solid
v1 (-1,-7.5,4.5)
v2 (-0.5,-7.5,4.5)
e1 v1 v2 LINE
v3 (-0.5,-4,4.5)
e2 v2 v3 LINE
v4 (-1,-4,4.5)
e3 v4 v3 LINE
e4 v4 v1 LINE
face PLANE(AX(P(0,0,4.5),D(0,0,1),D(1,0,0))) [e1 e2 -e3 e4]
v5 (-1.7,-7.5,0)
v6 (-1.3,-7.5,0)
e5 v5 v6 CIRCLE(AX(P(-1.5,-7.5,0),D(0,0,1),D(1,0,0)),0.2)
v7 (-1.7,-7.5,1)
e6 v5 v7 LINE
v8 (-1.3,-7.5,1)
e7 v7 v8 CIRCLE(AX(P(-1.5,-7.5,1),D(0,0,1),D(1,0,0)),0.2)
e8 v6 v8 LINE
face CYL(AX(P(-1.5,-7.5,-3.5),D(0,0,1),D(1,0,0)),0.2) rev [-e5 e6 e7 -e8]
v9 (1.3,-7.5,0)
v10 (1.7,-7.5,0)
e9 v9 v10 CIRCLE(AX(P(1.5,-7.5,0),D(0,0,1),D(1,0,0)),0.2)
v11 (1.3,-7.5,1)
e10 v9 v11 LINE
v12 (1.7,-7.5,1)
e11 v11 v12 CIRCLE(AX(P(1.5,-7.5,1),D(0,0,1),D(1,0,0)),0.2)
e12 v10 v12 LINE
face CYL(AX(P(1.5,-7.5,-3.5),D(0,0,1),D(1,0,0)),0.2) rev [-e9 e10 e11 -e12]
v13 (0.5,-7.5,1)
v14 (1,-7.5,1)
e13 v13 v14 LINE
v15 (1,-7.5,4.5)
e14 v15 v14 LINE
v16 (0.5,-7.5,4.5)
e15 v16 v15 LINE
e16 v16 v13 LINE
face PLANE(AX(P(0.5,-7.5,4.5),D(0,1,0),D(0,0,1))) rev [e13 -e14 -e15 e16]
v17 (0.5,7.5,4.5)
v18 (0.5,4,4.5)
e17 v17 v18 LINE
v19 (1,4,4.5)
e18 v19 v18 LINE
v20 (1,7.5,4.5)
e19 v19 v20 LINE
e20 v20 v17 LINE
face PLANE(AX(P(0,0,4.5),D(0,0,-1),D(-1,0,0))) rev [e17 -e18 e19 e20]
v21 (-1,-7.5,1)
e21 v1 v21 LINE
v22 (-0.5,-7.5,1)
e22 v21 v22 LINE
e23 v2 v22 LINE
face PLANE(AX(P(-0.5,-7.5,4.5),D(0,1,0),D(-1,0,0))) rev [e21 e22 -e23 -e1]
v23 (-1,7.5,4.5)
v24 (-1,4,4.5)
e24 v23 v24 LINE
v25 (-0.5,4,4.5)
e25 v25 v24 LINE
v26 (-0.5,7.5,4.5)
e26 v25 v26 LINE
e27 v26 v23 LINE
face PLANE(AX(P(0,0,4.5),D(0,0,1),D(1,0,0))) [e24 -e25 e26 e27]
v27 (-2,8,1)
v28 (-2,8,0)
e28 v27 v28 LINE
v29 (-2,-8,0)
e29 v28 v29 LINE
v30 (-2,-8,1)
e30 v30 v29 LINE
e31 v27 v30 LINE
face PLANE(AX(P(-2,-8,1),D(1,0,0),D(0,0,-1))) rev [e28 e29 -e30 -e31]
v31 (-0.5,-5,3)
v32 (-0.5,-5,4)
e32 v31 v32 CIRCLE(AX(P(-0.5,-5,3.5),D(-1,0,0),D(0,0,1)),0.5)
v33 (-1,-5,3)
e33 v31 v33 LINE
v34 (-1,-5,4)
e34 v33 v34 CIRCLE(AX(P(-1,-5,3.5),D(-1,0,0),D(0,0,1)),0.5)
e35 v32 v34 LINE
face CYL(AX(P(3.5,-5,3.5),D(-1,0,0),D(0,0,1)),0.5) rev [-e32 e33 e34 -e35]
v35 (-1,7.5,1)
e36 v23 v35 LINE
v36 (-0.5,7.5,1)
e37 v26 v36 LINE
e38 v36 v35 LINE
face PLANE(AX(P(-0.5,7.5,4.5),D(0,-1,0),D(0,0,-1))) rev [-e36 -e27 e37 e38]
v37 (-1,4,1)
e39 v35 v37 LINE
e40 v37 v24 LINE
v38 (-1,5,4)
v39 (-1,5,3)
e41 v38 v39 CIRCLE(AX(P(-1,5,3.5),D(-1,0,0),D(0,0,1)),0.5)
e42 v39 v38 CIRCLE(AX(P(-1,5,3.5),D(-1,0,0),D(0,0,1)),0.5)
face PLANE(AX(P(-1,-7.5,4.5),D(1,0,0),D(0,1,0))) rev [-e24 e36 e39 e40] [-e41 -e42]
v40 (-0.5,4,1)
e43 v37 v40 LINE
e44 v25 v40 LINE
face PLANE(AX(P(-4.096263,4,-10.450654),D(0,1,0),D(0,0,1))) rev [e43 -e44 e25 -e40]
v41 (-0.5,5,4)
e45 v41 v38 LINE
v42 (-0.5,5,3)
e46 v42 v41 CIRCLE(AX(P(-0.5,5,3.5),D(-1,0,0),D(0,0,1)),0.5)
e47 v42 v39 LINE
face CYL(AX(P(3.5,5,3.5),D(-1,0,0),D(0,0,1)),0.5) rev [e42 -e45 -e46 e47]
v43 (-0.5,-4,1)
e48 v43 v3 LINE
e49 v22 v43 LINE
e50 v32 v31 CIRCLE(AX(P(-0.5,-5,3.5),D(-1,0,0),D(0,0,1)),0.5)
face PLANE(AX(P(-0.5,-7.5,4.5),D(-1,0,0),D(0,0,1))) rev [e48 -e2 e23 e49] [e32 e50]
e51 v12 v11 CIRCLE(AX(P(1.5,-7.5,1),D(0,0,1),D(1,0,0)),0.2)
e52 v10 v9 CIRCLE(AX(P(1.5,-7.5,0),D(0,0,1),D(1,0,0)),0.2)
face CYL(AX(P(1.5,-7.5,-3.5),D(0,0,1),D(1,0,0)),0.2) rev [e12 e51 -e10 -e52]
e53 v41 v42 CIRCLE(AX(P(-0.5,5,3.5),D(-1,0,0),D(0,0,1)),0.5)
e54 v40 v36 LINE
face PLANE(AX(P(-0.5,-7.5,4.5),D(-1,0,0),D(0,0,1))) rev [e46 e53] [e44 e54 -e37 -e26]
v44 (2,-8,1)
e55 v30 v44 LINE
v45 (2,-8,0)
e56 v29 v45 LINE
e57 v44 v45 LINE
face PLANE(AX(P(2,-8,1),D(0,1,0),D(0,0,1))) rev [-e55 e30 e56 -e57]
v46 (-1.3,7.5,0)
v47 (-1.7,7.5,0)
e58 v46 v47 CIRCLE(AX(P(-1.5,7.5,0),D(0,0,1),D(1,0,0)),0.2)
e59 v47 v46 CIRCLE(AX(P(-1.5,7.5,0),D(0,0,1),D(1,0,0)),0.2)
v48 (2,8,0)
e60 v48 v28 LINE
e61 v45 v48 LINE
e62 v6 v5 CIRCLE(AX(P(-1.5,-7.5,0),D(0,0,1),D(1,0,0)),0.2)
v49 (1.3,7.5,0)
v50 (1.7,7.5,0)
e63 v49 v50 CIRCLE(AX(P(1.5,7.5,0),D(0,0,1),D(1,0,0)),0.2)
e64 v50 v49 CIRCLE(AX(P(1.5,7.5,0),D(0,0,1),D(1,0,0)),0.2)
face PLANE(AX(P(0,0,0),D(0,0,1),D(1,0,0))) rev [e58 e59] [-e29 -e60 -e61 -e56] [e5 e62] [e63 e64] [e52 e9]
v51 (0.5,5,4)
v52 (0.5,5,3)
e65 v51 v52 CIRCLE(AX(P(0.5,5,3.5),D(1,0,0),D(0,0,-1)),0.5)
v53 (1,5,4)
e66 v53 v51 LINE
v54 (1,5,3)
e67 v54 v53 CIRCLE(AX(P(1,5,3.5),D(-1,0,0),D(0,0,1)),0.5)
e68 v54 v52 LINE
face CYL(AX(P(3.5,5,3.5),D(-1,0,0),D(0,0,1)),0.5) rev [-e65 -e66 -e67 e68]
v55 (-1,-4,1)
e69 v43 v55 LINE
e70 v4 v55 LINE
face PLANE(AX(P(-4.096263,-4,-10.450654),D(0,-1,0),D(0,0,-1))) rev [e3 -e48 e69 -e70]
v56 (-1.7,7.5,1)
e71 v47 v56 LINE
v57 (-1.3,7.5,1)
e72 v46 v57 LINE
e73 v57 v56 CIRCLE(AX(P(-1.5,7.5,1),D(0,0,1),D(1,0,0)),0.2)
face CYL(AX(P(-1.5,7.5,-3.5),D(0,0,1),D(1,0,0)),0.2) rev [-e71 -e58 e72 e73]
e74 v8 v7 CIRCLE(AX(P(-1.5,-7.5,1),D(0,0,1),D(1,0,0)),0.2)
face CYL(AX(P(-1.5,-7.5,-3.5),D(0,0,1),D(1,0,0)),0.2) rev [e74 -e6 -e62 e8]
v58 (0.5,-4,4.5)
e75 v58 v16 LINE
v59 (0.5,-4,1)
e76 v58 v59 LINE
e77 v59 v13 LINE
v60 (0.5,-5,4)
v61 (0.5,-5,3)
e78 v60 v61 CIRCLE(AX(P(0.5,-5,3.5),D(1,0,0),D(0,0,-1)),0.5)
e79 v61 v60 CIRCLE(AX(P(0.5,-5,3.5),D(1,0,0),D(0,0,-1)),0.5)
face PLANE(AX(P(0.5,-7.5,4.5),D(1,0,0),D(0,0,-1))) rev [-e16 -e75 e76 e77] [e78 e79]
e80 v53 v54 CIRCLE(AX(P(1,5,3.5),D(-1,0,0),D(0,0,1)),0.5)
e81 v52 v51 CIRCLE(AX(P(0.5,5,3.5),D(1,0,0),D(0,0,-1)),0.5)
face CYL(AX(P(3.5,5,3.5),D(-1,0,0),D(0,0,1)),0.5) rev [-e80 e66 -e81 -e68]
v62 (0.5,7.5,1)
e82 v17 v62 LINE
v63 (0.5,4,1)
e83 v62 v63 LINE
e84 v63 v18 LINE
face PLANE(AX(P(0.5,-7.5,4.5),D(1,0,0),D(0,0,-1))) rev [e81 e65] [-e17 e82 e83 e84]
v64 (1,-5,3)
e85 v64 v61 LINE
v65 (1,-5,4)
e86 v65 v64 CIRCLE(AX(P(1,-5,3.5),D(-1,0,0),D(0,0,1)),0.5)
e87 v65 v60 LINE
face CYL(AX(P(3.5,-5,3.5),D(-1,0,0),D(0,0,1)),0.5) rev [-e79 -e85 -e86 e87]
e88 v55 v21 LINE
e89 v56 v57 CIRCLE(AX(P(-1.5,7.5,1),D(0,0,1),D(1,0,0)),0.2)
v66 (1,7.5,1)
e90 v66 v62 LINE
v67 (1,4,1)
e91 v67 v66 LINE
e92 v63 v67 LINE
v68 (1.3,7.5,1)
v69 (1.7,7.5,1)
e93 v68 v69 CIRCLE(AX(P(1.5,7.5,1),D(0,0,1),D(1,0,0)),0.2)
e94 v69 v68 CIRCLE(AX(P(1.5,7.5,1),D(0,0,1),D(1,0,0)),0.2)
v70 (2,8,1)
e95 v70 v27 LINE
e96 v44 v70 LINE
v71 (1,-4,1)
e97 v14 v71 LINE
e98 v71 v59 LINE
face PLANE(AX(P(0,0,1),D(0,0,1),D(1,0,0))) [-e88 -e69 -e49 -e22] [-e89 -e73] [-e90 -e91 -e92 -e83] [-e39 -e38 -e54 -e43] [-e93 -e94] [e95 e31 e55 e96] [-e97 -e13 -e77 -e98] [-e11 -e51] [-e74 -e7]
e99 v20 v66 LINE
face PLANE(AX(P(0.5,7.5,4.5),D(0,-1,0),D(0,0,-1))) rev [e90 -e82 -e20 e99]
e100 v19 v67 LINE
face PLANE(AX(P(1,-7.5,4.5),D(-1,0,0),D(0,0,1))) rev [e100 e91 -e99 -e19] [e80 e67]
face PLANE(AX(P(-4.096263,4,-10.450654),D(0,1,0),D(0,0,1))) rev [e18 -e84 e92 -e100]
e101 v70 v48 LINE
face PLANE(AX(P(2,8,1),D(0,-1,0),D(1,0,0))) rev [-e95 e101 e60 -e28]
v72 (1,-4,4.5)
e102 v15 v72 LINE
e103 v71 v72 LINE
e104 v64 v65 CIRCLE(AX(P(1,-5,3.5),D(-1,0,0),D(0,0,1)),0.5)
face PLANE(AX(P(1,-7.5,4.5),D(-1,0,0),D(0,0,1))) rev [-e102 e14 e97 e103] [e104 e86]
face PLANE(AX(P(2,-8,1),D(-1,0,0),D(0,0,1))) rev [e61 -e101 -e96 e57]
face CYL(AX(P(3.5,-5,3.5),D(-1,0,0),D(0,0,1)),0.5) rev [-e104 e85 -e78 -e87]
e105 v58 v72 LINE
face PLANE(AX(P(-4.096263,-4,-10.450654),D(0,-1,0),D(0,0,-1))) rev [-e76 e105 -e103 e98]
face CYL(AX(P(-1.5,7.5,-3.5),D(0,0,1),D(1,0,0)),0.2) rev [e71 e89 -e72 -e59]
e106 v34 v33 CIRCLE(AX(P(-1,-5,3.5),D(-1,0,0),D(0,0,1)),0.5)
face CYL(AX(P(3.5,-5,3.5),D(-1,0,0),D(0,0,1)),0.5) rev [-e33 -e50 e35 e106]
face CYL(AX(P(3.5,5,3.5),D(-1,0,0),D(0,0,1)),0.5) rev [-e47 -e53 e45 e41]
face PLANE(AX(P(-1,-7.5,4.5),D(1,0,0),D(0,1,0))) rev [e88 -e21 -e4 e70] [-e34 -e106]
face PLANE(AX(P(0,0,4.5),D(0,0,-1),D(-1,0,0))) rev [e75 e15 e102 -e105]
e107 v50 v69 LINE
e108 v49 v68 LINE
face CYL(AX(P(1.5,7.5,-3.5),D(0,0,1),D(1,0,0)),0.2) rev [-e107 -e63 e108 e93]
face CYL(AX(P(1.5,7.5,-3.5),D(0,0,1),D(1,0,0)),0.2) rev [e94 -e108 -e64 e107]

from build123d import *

# Parameters (mm, degrees)
SKETCH1_W           = 4
SKETCH1_H           = 16
BOSS_EXTRUDE1_DEPTH = 1
SKETCH2_W           = 0.5
SKETCH2_H           = 15
BOSS_EXTRUDE2_DEPTH = 3.5
SKETCH3_R           = 0.5
CUT_EXTRUDE1_DEPTH  = 4.5
SKETCH4_R           = 0.2
CUT_EXTRUDE2_DEPTH  = 4.5
SKETCH5_W           = 8.19252636
SKETCH5_H           = 8
CUT_EXTRUDE3_DEPTH  = 3.5


with BuildPart() as part:
    # Sketch1 → Boss-Extrude1 (new body)
    with BuildSketch(Plane.XY):
        Rectangle(SKETCH1_W, SKETCH1_H)
    extrude(amount=BOSS_EXTRUDE1_DEPTH)

    # Sketch2 → Boss-Extrude2 (add)
    with BuildSketch(Plane.XY.offset(1)):
        with Locations((0.75, 0)):
            Rectangle(SKETCH2_W, SKETCH2_H)
        with Locations((-0.75, 0)):
            Rectangle(SKETCH2_W, SKETCH2_H)
    extrude(amount=BOSS_EXTRUDE2_DEPTH)

    # Sketch3 → Cut-Extrude1 (cut)
    with BuildSketch(Plane.ZY.offset(1)):
        with Locations((3.5, 5)):
            Circle(SKETCH3_R)
        with Locations((3.5, -5)):
            Circle(SKETCH3_R)
    extrude(amount=-CUT_EXTRUDE1_DEPTH, mode=Mode.SUBTRACT)

    # Sketch4 → Cut-Extrude2 (cut)
    with BuildSketch(Plane.XY.offset(1)):
        with Locations((-1.5, 7.5)):
            Circle(SKETCH4_R)
        with Locations((-1.5, -7.5)):
            Circle(SKETCH4_R)
        with Locations((1.5, -7.5)):
            Circle(SKETCH4_R)
        with Locations((1.5, 7.5)):
            Circle(SKETCH4_R)
    extrude(amount=-CUT_EXTRUDE2_DEPTH, mode=Mode.SUBTRACT)

    # Sketch5 → Cut-Extrude3 (cut)
    with BuildSketch(Plane.XY.offset(4.5)):
        Rectangle(SKETCH5_W, SKETCH5_H)
    extrude(amount=-CUT_EXTRUDE3_DEPTH, mode=Mode.SUBTRACT)


solid = part.part
